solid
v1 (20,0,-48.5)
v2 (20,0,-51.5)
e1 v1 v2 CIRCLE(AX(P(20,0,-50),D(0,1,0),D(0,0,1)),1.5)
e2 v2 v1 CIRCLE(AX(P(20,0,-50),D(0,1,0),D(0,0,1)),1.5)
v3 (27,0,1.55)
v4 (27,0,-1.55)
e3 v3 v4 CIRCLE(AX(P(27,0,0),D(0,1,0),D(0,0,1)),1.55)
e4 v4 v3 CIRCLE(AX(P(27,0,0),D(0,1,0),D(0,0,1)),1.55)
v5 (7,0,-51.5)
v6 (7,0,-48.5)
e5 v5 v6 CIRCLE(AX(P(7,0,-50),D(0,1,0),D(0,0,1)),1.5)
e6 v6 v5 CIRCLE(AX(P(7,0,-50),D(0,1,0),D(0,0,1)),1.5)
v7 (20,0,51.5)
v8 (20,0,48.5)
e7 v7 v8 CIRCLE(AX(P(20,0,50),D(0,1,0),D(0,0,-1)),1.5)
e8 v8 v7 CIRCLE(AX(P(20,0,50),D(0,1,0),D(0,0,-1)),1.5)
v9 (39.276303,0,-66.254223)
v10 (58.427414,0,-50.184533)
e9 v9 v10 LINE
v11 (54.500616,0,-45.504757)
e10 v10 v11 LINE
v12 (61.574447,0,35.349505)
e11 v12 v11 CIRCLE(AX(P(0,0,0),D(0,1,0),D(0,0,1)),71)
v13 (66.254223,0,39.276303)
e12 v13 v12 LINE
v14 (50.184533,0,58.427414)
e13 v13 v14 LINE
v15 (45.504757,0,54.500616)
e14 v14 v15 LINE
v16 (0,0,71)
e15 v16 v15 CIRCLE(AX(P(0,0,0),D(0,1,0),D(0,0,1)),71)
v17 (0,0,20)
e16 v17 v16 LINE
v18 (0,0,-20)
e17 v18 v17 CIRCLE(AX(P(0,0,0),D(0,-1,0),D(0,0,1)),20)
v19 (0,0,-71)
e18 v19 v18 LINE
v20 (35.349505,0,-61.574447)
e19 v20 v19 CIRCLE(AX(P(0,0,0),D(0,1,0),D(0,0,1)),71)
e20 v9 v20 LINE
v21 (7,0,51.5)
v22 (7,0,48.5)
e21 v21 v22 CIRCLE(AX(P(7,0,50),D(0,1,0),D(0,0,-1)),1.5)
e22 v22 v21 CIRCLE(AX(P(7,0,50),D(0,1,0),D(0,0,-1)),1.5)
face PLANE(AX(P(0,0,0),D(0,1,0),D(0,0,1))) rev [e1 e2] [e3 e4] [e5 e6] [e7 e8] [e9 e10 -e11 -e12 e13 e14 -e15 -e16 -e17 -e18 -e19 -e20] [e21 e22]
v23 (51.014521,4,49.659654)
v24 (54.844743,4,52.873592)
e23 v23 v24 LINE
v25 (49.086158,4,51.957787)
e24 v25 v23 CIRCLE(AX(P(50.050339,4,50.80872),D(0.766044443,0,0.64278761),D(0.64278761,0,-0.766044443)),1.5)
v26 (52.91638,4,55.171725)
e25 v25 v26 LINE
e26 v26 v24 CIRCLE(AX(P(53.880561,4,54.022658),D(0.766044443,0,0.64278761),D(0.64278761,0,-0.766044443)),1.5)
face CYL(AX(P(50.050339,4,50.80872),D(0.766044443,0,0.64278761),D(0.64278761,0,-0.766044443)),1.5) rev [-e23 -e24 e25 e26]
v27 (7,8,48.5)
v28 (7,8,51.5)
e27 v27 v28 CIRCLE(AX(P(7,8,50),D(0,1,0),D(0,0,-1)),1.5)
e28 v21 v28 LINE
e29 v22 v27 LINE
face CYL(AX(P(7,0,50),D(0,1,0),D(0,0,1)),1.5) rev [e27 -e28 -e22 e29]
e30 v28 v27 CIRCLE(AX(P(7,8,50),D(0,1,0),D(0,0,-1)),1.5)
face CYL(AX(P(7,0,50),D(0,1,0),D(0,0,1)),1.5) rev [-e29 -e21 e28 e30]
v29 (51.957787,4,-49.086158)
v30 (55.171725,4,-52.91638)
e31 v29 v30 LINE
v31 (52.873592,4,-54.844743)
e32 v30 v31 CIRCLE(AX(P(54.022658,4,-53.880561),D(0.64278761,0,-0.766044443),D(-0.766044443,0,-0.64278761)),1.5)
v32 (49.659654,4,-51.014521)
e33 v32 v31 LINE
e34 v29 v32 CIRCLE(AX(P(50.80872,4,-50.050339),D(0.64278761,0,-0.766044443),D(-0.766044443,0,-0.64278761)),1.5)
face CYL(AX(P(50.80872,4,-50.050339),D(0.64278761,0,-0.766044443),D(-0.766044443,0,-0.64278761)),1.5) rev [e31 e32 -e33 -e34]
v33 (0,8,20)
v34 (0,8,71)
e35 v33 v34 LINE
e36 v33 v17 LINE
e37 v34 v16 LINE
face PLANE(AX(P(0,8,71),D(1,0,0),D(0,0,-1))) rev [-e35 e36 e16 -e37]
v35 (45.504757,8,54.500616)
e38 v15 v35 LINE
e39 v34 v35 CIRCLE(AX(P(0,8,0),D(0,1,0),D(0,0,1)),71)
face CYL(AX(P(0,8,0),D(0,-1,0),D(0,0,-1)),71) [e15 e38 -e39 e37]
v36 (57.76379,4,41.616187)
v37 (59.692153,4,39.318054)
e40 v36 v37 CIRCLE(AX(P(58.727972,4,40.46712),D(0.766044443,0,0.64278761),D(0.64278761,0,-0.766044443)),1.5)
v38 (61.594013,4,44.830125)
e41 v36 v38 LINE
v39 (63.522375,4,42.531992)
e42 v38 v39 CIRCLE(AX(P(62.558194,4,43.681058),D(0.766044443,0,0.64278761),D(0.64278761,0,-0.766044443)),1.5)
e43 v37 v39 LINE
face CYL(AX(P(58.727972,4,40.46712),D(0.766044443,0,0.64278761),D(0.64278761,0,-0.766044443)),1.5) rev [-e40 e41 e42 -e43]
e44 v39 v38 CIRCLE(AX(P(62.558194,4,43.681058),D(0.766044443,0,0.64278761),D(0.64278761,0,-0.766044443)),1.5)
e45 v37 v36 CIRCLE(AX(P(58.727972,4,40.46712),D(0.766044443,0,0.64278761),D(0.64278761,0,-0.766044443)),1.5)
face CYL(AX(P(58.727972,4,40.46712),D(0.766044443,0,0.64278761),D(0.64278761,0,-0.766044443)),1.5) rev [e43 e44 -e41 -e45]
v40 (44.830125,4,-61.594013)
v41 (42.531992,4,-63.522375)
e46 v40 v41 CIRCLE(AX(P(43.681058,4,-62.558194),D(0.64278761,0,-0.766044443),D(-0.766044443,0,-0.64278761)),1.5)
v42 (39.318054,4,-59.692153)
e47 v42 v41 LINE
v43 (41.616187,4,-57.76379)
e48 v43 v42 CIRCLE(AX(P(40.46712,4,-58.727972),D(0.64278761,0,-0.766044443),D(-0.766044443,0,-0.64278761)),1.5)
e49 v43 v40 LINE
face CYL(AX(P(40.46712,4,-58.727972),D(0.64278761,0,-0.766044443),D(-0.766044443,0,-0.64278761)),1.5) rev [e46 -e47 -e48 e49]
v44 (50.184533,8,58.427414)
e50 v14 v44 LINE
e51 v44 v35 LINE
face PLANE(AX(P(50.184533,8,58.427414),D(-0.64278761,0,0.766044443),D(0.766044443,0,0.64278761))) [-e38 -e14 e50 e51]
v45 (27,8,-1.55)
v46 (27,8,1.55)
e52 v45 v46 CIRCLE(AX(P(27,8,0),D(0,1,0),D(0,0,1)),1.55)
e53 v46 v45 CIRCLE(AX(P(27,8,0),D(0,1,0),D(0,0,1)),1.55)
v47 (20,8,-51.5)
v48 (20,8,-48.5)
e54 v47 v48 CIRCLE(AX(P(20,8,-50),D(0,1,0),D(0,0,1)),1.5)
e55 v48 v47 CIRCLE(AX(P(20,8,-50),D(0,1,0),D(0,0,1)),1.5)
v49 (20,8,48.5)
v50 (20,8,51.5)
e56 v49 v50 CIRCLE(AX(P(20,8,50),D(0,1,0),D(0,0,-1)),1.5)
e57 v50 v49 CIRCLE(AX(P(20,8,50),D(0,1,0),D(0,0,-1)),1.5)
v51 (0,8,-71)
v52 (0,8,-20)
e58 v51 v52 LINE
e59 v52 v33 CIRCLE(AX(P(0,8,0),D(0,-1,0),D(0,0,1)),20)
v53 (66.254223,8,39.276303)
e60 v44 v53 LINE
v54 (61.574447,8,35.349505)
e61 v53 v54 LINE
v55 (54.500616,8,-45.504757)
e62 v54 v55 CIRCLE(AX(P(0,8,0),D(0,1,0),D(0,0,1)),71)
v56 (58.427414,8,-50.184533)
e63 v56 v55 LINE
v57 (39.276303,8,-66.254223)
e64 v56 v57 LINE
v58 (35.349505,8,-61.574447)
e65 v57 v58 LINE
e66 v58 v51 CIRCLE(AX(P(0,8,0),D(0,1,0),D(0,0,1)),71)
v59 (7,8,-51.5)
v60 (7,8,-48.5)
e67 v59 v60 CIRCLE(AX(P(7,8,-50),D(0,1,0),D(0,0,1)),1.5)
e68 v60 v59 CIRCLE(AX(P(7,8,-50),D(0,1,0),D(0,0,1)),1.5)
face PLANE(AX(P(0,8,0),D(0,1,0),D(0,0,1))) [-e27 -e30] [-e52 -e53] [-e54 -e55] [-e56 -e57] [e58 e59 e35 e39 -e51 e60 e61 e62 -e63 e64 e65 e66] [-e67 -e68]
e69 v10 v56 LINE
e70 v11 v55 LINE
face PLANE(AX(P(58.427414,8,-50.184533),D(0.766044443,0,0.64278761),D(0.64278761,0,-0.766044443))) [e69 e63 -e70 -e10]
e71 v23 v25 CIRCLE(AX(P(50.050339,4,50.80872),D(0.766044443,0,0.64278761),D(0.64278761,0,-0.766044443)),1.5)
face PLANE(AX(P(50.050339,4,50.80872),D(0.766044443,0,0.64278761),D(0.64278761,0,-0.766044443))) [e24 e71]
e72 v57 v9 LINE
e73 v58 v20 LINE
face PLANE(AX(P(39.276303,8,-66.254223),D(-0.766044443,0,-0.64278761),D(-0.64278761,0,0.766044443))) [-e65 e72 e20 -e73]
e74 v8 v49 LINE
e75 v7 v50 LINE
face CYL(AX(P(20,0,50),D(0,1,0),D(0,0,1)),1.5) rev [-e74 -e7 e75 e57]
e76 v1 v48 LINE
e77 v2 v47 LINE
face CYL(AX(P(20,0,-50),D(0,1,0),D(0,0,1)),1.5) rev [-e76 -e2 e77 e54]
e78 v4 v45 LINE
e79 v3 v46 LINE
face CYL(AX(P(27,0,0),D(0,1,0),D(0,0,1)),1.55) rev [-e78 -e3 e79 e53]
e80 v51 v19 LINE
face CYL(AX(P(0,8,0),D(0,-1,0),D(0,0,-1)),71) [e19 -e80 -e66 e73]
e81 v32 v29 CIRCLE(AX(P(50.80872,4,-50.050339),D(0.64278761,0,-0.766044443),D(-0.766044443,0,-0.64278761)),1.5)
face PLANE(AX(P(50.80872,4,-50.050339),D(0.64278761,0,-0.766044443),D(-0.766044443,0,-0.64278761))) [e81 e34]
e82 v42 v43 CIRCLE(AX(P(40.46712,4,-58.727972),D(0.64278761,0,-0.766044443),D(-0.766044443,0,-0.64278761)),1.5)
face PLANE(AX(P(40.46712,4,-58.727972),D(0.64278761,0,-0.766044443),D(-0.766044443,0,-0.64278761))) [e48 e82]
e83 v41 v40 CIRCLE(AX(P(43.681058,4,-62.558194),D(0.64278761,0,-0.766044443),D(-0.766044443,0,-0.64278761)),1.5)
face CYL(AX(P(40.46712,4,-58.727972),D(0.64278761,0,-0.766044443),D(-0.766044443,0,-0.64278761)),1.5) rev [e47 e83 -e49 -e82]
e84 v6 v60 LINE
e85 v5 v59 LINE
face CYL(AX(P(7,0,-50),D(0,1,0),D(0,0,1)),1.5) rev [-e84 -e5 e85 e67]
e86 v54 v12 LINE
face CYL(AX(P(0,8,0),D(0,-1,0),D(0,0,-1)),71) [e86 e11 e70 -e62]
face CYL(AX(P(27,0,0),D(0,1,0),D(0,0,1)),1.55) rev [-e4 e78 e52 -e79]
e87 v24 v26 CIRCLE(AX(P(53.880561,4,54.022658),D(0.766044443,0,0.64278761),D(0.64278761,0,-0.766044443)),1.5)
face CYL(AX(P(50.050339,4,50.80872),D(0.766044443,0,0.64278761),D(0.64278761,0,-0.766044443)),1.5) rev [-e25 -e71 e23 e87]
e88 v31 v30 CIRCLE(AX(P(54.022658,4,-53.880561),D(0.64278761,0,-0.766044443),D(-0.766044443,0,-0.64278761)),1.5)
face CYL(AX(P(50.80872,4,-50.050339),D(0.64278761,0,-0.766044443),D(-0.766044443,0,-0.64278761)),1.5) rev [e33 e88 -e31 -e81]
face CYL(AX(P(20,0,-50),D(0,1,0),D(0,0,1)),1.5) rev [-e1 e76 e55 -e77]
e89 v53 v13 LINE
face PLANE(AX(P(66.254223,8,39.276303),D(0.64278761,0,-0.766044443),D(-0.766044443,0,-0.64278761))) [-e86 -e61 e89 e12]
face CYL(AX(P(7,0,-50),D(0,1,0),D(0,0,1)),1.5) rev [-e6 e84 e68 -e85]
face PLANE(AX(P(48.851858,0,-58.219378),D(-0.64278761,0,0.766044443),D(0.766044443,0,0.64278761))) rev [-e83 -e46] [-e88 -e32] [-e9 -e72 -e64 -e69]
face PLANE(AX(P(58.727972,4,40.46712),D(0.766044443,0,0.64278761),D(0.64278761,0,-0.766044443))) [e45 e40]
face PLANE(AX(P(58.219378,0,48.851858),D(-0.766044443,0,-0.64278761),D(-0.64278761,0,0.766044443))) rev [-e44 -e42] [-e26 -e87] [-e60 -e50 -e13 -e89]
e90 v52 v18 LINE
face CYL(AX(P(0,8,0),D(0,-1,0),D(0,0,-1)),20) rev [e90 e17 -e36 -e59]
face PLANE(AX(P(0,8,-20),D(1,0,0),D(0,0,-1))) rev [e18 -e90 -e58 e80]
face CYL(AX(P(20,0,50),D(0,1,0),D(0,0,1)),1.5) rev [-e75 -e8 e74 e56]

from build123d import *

# Parameters (mm, degrees)
BOSS_EXTRUDE1_DEPTH = 8
SKETCH2_R           = 1.5
CUT_EXTRUDE1_DEPTH  = 101.727354775
BOSS_EXTRUDE2_START = -71
SKETCH3_W           = 8
SKETCH3_H           = 25
BOSS_EXTRUDE2_DEPTH = 5
SKETCH4_R           = 1.5
CUT_EXTRUDE2_DEPTH  = 5
CIRPATTERN1_COUNT   = 2
CIRPATTERN1_ANGLE   = 90
SKETCH5_R           = 1.55
CUT_EXTRUDE3_DEPTH  = 101.727354775


with BuildPart() as part:
    # Sketch1 → Boss-Extrude1 (new body)
    with BuildSketch(Plane(origin=(0, 0, 0), x_dir=(1, 0, 0), z_dir=(0, 1, 0))):
        with BuildLine():
            Line((0, -71), (0, -20))
            ThreePointArc((0, -20), (20, 0), (0, 20))
            Line((0, 20), (0, 71))
            ThreePointArc((0, 71), (71, 0), (0, -71))
        make_face()
    extrude(amount=BOSS_EXTRUDE1_DEPTH)

    # Sketch2 → Cut-Extrude1 (cut, through all)
    with BuildSketch(Plane(origin=(0, 8, 0), x_dir=(1, 0, 0), z_dir=(0, 1, 0))):
        with Locations(Location((7, 50, 0), (0, 0, 270))):
            Circle(SKETCH2_R)
        with Locations(Location((20, 50, 0), (0, 0, 270))):
            Circle(SKETCH2_R)
        with Locations(Location((20, -50, 0), (0, 0, 90))):
            Circle(SKETCH2_R)
        with Locations(Location((7, -50, 0), (0, 0, 90))):
            Circle(SKETCH2_R)
    extrude(amount=-CUT_EXTRUDE1_DEPTH, mode=Mode.SUBTRACT)

    # Sketch3 → Boss-Extrude2 (add, symmetric)
    with BuildSketch(Plane(origin=(0, 0, 0), x_dir=(0, -1, 0), z_dir=(-0.6427876096865403, 0, 0.7660444431189772)).offset(BOSS_EXTRUDE2_START)):
        with Locations((-4, 0)):
            Rectangle(SKETCH3_W, SKETCH3_H)
    boss_extrude2 = extrude(amount=BOSS_EXTRUDE2_DEPTH, both=True)

    # Sketch4 → Cut-Extrude2 (cut)
    with BuildSketch(Plane(origin=(48.851858336, 0, -58.219377677), x_dir=(-0.7660444431189771, 0, -0.6427876096865404), z_dir=(0.6427876096865404, 0, -0.7660444431189771))):
        with Locations((-6.75, 4)):
            Circle(SKETCH4_R)
        with Locations((6.75, 4)):
            Circle(SKETCH4_R)
    cut_extrude2 = extrude(amount=-CUT_EXTRUDE2_DEPTH, mode=Mode.SUBTRACT)

    # CirPattern1: Boss-Extrude2, Cut-Extrude2 ×2 about axis
    cirpattern1_axis = Axis((0, 0, 0), (0, -1, 0))
    add([boss_extrude2.rotate(cirpattern1_axis, i * CIRPATTERN1_ANGLE / (CIRPATTERN1_COUNT - 1)) for i in range(1, CIRPATTERN1_COUNT)])
    add([cut_extrude2.rotate(cirpattern1_axis, i * CIRPATTERN1_ANGLE / (CIRPATTERN1_COUNT - 1)) for i in range(1, CIRPATTERN1_COUNT)], mode=Mode.SUBTRACT)

    # Sketch5 → Cut-Extrude3 (cut, through all)
    with BuildSketch(Plane(origin=(0, 8, 0), x_dir=(1, 0, 0), z_dir=(0, 1, 0))):
        with Locations(Location((27, 0, 0), (0, 0, 270))):
            Circle(SKETCH5_R)
    extrude(amount=-CUT_EXTRUDE3_DEPTH, mode=Mode.SUBTRACT)


solid = part.part
